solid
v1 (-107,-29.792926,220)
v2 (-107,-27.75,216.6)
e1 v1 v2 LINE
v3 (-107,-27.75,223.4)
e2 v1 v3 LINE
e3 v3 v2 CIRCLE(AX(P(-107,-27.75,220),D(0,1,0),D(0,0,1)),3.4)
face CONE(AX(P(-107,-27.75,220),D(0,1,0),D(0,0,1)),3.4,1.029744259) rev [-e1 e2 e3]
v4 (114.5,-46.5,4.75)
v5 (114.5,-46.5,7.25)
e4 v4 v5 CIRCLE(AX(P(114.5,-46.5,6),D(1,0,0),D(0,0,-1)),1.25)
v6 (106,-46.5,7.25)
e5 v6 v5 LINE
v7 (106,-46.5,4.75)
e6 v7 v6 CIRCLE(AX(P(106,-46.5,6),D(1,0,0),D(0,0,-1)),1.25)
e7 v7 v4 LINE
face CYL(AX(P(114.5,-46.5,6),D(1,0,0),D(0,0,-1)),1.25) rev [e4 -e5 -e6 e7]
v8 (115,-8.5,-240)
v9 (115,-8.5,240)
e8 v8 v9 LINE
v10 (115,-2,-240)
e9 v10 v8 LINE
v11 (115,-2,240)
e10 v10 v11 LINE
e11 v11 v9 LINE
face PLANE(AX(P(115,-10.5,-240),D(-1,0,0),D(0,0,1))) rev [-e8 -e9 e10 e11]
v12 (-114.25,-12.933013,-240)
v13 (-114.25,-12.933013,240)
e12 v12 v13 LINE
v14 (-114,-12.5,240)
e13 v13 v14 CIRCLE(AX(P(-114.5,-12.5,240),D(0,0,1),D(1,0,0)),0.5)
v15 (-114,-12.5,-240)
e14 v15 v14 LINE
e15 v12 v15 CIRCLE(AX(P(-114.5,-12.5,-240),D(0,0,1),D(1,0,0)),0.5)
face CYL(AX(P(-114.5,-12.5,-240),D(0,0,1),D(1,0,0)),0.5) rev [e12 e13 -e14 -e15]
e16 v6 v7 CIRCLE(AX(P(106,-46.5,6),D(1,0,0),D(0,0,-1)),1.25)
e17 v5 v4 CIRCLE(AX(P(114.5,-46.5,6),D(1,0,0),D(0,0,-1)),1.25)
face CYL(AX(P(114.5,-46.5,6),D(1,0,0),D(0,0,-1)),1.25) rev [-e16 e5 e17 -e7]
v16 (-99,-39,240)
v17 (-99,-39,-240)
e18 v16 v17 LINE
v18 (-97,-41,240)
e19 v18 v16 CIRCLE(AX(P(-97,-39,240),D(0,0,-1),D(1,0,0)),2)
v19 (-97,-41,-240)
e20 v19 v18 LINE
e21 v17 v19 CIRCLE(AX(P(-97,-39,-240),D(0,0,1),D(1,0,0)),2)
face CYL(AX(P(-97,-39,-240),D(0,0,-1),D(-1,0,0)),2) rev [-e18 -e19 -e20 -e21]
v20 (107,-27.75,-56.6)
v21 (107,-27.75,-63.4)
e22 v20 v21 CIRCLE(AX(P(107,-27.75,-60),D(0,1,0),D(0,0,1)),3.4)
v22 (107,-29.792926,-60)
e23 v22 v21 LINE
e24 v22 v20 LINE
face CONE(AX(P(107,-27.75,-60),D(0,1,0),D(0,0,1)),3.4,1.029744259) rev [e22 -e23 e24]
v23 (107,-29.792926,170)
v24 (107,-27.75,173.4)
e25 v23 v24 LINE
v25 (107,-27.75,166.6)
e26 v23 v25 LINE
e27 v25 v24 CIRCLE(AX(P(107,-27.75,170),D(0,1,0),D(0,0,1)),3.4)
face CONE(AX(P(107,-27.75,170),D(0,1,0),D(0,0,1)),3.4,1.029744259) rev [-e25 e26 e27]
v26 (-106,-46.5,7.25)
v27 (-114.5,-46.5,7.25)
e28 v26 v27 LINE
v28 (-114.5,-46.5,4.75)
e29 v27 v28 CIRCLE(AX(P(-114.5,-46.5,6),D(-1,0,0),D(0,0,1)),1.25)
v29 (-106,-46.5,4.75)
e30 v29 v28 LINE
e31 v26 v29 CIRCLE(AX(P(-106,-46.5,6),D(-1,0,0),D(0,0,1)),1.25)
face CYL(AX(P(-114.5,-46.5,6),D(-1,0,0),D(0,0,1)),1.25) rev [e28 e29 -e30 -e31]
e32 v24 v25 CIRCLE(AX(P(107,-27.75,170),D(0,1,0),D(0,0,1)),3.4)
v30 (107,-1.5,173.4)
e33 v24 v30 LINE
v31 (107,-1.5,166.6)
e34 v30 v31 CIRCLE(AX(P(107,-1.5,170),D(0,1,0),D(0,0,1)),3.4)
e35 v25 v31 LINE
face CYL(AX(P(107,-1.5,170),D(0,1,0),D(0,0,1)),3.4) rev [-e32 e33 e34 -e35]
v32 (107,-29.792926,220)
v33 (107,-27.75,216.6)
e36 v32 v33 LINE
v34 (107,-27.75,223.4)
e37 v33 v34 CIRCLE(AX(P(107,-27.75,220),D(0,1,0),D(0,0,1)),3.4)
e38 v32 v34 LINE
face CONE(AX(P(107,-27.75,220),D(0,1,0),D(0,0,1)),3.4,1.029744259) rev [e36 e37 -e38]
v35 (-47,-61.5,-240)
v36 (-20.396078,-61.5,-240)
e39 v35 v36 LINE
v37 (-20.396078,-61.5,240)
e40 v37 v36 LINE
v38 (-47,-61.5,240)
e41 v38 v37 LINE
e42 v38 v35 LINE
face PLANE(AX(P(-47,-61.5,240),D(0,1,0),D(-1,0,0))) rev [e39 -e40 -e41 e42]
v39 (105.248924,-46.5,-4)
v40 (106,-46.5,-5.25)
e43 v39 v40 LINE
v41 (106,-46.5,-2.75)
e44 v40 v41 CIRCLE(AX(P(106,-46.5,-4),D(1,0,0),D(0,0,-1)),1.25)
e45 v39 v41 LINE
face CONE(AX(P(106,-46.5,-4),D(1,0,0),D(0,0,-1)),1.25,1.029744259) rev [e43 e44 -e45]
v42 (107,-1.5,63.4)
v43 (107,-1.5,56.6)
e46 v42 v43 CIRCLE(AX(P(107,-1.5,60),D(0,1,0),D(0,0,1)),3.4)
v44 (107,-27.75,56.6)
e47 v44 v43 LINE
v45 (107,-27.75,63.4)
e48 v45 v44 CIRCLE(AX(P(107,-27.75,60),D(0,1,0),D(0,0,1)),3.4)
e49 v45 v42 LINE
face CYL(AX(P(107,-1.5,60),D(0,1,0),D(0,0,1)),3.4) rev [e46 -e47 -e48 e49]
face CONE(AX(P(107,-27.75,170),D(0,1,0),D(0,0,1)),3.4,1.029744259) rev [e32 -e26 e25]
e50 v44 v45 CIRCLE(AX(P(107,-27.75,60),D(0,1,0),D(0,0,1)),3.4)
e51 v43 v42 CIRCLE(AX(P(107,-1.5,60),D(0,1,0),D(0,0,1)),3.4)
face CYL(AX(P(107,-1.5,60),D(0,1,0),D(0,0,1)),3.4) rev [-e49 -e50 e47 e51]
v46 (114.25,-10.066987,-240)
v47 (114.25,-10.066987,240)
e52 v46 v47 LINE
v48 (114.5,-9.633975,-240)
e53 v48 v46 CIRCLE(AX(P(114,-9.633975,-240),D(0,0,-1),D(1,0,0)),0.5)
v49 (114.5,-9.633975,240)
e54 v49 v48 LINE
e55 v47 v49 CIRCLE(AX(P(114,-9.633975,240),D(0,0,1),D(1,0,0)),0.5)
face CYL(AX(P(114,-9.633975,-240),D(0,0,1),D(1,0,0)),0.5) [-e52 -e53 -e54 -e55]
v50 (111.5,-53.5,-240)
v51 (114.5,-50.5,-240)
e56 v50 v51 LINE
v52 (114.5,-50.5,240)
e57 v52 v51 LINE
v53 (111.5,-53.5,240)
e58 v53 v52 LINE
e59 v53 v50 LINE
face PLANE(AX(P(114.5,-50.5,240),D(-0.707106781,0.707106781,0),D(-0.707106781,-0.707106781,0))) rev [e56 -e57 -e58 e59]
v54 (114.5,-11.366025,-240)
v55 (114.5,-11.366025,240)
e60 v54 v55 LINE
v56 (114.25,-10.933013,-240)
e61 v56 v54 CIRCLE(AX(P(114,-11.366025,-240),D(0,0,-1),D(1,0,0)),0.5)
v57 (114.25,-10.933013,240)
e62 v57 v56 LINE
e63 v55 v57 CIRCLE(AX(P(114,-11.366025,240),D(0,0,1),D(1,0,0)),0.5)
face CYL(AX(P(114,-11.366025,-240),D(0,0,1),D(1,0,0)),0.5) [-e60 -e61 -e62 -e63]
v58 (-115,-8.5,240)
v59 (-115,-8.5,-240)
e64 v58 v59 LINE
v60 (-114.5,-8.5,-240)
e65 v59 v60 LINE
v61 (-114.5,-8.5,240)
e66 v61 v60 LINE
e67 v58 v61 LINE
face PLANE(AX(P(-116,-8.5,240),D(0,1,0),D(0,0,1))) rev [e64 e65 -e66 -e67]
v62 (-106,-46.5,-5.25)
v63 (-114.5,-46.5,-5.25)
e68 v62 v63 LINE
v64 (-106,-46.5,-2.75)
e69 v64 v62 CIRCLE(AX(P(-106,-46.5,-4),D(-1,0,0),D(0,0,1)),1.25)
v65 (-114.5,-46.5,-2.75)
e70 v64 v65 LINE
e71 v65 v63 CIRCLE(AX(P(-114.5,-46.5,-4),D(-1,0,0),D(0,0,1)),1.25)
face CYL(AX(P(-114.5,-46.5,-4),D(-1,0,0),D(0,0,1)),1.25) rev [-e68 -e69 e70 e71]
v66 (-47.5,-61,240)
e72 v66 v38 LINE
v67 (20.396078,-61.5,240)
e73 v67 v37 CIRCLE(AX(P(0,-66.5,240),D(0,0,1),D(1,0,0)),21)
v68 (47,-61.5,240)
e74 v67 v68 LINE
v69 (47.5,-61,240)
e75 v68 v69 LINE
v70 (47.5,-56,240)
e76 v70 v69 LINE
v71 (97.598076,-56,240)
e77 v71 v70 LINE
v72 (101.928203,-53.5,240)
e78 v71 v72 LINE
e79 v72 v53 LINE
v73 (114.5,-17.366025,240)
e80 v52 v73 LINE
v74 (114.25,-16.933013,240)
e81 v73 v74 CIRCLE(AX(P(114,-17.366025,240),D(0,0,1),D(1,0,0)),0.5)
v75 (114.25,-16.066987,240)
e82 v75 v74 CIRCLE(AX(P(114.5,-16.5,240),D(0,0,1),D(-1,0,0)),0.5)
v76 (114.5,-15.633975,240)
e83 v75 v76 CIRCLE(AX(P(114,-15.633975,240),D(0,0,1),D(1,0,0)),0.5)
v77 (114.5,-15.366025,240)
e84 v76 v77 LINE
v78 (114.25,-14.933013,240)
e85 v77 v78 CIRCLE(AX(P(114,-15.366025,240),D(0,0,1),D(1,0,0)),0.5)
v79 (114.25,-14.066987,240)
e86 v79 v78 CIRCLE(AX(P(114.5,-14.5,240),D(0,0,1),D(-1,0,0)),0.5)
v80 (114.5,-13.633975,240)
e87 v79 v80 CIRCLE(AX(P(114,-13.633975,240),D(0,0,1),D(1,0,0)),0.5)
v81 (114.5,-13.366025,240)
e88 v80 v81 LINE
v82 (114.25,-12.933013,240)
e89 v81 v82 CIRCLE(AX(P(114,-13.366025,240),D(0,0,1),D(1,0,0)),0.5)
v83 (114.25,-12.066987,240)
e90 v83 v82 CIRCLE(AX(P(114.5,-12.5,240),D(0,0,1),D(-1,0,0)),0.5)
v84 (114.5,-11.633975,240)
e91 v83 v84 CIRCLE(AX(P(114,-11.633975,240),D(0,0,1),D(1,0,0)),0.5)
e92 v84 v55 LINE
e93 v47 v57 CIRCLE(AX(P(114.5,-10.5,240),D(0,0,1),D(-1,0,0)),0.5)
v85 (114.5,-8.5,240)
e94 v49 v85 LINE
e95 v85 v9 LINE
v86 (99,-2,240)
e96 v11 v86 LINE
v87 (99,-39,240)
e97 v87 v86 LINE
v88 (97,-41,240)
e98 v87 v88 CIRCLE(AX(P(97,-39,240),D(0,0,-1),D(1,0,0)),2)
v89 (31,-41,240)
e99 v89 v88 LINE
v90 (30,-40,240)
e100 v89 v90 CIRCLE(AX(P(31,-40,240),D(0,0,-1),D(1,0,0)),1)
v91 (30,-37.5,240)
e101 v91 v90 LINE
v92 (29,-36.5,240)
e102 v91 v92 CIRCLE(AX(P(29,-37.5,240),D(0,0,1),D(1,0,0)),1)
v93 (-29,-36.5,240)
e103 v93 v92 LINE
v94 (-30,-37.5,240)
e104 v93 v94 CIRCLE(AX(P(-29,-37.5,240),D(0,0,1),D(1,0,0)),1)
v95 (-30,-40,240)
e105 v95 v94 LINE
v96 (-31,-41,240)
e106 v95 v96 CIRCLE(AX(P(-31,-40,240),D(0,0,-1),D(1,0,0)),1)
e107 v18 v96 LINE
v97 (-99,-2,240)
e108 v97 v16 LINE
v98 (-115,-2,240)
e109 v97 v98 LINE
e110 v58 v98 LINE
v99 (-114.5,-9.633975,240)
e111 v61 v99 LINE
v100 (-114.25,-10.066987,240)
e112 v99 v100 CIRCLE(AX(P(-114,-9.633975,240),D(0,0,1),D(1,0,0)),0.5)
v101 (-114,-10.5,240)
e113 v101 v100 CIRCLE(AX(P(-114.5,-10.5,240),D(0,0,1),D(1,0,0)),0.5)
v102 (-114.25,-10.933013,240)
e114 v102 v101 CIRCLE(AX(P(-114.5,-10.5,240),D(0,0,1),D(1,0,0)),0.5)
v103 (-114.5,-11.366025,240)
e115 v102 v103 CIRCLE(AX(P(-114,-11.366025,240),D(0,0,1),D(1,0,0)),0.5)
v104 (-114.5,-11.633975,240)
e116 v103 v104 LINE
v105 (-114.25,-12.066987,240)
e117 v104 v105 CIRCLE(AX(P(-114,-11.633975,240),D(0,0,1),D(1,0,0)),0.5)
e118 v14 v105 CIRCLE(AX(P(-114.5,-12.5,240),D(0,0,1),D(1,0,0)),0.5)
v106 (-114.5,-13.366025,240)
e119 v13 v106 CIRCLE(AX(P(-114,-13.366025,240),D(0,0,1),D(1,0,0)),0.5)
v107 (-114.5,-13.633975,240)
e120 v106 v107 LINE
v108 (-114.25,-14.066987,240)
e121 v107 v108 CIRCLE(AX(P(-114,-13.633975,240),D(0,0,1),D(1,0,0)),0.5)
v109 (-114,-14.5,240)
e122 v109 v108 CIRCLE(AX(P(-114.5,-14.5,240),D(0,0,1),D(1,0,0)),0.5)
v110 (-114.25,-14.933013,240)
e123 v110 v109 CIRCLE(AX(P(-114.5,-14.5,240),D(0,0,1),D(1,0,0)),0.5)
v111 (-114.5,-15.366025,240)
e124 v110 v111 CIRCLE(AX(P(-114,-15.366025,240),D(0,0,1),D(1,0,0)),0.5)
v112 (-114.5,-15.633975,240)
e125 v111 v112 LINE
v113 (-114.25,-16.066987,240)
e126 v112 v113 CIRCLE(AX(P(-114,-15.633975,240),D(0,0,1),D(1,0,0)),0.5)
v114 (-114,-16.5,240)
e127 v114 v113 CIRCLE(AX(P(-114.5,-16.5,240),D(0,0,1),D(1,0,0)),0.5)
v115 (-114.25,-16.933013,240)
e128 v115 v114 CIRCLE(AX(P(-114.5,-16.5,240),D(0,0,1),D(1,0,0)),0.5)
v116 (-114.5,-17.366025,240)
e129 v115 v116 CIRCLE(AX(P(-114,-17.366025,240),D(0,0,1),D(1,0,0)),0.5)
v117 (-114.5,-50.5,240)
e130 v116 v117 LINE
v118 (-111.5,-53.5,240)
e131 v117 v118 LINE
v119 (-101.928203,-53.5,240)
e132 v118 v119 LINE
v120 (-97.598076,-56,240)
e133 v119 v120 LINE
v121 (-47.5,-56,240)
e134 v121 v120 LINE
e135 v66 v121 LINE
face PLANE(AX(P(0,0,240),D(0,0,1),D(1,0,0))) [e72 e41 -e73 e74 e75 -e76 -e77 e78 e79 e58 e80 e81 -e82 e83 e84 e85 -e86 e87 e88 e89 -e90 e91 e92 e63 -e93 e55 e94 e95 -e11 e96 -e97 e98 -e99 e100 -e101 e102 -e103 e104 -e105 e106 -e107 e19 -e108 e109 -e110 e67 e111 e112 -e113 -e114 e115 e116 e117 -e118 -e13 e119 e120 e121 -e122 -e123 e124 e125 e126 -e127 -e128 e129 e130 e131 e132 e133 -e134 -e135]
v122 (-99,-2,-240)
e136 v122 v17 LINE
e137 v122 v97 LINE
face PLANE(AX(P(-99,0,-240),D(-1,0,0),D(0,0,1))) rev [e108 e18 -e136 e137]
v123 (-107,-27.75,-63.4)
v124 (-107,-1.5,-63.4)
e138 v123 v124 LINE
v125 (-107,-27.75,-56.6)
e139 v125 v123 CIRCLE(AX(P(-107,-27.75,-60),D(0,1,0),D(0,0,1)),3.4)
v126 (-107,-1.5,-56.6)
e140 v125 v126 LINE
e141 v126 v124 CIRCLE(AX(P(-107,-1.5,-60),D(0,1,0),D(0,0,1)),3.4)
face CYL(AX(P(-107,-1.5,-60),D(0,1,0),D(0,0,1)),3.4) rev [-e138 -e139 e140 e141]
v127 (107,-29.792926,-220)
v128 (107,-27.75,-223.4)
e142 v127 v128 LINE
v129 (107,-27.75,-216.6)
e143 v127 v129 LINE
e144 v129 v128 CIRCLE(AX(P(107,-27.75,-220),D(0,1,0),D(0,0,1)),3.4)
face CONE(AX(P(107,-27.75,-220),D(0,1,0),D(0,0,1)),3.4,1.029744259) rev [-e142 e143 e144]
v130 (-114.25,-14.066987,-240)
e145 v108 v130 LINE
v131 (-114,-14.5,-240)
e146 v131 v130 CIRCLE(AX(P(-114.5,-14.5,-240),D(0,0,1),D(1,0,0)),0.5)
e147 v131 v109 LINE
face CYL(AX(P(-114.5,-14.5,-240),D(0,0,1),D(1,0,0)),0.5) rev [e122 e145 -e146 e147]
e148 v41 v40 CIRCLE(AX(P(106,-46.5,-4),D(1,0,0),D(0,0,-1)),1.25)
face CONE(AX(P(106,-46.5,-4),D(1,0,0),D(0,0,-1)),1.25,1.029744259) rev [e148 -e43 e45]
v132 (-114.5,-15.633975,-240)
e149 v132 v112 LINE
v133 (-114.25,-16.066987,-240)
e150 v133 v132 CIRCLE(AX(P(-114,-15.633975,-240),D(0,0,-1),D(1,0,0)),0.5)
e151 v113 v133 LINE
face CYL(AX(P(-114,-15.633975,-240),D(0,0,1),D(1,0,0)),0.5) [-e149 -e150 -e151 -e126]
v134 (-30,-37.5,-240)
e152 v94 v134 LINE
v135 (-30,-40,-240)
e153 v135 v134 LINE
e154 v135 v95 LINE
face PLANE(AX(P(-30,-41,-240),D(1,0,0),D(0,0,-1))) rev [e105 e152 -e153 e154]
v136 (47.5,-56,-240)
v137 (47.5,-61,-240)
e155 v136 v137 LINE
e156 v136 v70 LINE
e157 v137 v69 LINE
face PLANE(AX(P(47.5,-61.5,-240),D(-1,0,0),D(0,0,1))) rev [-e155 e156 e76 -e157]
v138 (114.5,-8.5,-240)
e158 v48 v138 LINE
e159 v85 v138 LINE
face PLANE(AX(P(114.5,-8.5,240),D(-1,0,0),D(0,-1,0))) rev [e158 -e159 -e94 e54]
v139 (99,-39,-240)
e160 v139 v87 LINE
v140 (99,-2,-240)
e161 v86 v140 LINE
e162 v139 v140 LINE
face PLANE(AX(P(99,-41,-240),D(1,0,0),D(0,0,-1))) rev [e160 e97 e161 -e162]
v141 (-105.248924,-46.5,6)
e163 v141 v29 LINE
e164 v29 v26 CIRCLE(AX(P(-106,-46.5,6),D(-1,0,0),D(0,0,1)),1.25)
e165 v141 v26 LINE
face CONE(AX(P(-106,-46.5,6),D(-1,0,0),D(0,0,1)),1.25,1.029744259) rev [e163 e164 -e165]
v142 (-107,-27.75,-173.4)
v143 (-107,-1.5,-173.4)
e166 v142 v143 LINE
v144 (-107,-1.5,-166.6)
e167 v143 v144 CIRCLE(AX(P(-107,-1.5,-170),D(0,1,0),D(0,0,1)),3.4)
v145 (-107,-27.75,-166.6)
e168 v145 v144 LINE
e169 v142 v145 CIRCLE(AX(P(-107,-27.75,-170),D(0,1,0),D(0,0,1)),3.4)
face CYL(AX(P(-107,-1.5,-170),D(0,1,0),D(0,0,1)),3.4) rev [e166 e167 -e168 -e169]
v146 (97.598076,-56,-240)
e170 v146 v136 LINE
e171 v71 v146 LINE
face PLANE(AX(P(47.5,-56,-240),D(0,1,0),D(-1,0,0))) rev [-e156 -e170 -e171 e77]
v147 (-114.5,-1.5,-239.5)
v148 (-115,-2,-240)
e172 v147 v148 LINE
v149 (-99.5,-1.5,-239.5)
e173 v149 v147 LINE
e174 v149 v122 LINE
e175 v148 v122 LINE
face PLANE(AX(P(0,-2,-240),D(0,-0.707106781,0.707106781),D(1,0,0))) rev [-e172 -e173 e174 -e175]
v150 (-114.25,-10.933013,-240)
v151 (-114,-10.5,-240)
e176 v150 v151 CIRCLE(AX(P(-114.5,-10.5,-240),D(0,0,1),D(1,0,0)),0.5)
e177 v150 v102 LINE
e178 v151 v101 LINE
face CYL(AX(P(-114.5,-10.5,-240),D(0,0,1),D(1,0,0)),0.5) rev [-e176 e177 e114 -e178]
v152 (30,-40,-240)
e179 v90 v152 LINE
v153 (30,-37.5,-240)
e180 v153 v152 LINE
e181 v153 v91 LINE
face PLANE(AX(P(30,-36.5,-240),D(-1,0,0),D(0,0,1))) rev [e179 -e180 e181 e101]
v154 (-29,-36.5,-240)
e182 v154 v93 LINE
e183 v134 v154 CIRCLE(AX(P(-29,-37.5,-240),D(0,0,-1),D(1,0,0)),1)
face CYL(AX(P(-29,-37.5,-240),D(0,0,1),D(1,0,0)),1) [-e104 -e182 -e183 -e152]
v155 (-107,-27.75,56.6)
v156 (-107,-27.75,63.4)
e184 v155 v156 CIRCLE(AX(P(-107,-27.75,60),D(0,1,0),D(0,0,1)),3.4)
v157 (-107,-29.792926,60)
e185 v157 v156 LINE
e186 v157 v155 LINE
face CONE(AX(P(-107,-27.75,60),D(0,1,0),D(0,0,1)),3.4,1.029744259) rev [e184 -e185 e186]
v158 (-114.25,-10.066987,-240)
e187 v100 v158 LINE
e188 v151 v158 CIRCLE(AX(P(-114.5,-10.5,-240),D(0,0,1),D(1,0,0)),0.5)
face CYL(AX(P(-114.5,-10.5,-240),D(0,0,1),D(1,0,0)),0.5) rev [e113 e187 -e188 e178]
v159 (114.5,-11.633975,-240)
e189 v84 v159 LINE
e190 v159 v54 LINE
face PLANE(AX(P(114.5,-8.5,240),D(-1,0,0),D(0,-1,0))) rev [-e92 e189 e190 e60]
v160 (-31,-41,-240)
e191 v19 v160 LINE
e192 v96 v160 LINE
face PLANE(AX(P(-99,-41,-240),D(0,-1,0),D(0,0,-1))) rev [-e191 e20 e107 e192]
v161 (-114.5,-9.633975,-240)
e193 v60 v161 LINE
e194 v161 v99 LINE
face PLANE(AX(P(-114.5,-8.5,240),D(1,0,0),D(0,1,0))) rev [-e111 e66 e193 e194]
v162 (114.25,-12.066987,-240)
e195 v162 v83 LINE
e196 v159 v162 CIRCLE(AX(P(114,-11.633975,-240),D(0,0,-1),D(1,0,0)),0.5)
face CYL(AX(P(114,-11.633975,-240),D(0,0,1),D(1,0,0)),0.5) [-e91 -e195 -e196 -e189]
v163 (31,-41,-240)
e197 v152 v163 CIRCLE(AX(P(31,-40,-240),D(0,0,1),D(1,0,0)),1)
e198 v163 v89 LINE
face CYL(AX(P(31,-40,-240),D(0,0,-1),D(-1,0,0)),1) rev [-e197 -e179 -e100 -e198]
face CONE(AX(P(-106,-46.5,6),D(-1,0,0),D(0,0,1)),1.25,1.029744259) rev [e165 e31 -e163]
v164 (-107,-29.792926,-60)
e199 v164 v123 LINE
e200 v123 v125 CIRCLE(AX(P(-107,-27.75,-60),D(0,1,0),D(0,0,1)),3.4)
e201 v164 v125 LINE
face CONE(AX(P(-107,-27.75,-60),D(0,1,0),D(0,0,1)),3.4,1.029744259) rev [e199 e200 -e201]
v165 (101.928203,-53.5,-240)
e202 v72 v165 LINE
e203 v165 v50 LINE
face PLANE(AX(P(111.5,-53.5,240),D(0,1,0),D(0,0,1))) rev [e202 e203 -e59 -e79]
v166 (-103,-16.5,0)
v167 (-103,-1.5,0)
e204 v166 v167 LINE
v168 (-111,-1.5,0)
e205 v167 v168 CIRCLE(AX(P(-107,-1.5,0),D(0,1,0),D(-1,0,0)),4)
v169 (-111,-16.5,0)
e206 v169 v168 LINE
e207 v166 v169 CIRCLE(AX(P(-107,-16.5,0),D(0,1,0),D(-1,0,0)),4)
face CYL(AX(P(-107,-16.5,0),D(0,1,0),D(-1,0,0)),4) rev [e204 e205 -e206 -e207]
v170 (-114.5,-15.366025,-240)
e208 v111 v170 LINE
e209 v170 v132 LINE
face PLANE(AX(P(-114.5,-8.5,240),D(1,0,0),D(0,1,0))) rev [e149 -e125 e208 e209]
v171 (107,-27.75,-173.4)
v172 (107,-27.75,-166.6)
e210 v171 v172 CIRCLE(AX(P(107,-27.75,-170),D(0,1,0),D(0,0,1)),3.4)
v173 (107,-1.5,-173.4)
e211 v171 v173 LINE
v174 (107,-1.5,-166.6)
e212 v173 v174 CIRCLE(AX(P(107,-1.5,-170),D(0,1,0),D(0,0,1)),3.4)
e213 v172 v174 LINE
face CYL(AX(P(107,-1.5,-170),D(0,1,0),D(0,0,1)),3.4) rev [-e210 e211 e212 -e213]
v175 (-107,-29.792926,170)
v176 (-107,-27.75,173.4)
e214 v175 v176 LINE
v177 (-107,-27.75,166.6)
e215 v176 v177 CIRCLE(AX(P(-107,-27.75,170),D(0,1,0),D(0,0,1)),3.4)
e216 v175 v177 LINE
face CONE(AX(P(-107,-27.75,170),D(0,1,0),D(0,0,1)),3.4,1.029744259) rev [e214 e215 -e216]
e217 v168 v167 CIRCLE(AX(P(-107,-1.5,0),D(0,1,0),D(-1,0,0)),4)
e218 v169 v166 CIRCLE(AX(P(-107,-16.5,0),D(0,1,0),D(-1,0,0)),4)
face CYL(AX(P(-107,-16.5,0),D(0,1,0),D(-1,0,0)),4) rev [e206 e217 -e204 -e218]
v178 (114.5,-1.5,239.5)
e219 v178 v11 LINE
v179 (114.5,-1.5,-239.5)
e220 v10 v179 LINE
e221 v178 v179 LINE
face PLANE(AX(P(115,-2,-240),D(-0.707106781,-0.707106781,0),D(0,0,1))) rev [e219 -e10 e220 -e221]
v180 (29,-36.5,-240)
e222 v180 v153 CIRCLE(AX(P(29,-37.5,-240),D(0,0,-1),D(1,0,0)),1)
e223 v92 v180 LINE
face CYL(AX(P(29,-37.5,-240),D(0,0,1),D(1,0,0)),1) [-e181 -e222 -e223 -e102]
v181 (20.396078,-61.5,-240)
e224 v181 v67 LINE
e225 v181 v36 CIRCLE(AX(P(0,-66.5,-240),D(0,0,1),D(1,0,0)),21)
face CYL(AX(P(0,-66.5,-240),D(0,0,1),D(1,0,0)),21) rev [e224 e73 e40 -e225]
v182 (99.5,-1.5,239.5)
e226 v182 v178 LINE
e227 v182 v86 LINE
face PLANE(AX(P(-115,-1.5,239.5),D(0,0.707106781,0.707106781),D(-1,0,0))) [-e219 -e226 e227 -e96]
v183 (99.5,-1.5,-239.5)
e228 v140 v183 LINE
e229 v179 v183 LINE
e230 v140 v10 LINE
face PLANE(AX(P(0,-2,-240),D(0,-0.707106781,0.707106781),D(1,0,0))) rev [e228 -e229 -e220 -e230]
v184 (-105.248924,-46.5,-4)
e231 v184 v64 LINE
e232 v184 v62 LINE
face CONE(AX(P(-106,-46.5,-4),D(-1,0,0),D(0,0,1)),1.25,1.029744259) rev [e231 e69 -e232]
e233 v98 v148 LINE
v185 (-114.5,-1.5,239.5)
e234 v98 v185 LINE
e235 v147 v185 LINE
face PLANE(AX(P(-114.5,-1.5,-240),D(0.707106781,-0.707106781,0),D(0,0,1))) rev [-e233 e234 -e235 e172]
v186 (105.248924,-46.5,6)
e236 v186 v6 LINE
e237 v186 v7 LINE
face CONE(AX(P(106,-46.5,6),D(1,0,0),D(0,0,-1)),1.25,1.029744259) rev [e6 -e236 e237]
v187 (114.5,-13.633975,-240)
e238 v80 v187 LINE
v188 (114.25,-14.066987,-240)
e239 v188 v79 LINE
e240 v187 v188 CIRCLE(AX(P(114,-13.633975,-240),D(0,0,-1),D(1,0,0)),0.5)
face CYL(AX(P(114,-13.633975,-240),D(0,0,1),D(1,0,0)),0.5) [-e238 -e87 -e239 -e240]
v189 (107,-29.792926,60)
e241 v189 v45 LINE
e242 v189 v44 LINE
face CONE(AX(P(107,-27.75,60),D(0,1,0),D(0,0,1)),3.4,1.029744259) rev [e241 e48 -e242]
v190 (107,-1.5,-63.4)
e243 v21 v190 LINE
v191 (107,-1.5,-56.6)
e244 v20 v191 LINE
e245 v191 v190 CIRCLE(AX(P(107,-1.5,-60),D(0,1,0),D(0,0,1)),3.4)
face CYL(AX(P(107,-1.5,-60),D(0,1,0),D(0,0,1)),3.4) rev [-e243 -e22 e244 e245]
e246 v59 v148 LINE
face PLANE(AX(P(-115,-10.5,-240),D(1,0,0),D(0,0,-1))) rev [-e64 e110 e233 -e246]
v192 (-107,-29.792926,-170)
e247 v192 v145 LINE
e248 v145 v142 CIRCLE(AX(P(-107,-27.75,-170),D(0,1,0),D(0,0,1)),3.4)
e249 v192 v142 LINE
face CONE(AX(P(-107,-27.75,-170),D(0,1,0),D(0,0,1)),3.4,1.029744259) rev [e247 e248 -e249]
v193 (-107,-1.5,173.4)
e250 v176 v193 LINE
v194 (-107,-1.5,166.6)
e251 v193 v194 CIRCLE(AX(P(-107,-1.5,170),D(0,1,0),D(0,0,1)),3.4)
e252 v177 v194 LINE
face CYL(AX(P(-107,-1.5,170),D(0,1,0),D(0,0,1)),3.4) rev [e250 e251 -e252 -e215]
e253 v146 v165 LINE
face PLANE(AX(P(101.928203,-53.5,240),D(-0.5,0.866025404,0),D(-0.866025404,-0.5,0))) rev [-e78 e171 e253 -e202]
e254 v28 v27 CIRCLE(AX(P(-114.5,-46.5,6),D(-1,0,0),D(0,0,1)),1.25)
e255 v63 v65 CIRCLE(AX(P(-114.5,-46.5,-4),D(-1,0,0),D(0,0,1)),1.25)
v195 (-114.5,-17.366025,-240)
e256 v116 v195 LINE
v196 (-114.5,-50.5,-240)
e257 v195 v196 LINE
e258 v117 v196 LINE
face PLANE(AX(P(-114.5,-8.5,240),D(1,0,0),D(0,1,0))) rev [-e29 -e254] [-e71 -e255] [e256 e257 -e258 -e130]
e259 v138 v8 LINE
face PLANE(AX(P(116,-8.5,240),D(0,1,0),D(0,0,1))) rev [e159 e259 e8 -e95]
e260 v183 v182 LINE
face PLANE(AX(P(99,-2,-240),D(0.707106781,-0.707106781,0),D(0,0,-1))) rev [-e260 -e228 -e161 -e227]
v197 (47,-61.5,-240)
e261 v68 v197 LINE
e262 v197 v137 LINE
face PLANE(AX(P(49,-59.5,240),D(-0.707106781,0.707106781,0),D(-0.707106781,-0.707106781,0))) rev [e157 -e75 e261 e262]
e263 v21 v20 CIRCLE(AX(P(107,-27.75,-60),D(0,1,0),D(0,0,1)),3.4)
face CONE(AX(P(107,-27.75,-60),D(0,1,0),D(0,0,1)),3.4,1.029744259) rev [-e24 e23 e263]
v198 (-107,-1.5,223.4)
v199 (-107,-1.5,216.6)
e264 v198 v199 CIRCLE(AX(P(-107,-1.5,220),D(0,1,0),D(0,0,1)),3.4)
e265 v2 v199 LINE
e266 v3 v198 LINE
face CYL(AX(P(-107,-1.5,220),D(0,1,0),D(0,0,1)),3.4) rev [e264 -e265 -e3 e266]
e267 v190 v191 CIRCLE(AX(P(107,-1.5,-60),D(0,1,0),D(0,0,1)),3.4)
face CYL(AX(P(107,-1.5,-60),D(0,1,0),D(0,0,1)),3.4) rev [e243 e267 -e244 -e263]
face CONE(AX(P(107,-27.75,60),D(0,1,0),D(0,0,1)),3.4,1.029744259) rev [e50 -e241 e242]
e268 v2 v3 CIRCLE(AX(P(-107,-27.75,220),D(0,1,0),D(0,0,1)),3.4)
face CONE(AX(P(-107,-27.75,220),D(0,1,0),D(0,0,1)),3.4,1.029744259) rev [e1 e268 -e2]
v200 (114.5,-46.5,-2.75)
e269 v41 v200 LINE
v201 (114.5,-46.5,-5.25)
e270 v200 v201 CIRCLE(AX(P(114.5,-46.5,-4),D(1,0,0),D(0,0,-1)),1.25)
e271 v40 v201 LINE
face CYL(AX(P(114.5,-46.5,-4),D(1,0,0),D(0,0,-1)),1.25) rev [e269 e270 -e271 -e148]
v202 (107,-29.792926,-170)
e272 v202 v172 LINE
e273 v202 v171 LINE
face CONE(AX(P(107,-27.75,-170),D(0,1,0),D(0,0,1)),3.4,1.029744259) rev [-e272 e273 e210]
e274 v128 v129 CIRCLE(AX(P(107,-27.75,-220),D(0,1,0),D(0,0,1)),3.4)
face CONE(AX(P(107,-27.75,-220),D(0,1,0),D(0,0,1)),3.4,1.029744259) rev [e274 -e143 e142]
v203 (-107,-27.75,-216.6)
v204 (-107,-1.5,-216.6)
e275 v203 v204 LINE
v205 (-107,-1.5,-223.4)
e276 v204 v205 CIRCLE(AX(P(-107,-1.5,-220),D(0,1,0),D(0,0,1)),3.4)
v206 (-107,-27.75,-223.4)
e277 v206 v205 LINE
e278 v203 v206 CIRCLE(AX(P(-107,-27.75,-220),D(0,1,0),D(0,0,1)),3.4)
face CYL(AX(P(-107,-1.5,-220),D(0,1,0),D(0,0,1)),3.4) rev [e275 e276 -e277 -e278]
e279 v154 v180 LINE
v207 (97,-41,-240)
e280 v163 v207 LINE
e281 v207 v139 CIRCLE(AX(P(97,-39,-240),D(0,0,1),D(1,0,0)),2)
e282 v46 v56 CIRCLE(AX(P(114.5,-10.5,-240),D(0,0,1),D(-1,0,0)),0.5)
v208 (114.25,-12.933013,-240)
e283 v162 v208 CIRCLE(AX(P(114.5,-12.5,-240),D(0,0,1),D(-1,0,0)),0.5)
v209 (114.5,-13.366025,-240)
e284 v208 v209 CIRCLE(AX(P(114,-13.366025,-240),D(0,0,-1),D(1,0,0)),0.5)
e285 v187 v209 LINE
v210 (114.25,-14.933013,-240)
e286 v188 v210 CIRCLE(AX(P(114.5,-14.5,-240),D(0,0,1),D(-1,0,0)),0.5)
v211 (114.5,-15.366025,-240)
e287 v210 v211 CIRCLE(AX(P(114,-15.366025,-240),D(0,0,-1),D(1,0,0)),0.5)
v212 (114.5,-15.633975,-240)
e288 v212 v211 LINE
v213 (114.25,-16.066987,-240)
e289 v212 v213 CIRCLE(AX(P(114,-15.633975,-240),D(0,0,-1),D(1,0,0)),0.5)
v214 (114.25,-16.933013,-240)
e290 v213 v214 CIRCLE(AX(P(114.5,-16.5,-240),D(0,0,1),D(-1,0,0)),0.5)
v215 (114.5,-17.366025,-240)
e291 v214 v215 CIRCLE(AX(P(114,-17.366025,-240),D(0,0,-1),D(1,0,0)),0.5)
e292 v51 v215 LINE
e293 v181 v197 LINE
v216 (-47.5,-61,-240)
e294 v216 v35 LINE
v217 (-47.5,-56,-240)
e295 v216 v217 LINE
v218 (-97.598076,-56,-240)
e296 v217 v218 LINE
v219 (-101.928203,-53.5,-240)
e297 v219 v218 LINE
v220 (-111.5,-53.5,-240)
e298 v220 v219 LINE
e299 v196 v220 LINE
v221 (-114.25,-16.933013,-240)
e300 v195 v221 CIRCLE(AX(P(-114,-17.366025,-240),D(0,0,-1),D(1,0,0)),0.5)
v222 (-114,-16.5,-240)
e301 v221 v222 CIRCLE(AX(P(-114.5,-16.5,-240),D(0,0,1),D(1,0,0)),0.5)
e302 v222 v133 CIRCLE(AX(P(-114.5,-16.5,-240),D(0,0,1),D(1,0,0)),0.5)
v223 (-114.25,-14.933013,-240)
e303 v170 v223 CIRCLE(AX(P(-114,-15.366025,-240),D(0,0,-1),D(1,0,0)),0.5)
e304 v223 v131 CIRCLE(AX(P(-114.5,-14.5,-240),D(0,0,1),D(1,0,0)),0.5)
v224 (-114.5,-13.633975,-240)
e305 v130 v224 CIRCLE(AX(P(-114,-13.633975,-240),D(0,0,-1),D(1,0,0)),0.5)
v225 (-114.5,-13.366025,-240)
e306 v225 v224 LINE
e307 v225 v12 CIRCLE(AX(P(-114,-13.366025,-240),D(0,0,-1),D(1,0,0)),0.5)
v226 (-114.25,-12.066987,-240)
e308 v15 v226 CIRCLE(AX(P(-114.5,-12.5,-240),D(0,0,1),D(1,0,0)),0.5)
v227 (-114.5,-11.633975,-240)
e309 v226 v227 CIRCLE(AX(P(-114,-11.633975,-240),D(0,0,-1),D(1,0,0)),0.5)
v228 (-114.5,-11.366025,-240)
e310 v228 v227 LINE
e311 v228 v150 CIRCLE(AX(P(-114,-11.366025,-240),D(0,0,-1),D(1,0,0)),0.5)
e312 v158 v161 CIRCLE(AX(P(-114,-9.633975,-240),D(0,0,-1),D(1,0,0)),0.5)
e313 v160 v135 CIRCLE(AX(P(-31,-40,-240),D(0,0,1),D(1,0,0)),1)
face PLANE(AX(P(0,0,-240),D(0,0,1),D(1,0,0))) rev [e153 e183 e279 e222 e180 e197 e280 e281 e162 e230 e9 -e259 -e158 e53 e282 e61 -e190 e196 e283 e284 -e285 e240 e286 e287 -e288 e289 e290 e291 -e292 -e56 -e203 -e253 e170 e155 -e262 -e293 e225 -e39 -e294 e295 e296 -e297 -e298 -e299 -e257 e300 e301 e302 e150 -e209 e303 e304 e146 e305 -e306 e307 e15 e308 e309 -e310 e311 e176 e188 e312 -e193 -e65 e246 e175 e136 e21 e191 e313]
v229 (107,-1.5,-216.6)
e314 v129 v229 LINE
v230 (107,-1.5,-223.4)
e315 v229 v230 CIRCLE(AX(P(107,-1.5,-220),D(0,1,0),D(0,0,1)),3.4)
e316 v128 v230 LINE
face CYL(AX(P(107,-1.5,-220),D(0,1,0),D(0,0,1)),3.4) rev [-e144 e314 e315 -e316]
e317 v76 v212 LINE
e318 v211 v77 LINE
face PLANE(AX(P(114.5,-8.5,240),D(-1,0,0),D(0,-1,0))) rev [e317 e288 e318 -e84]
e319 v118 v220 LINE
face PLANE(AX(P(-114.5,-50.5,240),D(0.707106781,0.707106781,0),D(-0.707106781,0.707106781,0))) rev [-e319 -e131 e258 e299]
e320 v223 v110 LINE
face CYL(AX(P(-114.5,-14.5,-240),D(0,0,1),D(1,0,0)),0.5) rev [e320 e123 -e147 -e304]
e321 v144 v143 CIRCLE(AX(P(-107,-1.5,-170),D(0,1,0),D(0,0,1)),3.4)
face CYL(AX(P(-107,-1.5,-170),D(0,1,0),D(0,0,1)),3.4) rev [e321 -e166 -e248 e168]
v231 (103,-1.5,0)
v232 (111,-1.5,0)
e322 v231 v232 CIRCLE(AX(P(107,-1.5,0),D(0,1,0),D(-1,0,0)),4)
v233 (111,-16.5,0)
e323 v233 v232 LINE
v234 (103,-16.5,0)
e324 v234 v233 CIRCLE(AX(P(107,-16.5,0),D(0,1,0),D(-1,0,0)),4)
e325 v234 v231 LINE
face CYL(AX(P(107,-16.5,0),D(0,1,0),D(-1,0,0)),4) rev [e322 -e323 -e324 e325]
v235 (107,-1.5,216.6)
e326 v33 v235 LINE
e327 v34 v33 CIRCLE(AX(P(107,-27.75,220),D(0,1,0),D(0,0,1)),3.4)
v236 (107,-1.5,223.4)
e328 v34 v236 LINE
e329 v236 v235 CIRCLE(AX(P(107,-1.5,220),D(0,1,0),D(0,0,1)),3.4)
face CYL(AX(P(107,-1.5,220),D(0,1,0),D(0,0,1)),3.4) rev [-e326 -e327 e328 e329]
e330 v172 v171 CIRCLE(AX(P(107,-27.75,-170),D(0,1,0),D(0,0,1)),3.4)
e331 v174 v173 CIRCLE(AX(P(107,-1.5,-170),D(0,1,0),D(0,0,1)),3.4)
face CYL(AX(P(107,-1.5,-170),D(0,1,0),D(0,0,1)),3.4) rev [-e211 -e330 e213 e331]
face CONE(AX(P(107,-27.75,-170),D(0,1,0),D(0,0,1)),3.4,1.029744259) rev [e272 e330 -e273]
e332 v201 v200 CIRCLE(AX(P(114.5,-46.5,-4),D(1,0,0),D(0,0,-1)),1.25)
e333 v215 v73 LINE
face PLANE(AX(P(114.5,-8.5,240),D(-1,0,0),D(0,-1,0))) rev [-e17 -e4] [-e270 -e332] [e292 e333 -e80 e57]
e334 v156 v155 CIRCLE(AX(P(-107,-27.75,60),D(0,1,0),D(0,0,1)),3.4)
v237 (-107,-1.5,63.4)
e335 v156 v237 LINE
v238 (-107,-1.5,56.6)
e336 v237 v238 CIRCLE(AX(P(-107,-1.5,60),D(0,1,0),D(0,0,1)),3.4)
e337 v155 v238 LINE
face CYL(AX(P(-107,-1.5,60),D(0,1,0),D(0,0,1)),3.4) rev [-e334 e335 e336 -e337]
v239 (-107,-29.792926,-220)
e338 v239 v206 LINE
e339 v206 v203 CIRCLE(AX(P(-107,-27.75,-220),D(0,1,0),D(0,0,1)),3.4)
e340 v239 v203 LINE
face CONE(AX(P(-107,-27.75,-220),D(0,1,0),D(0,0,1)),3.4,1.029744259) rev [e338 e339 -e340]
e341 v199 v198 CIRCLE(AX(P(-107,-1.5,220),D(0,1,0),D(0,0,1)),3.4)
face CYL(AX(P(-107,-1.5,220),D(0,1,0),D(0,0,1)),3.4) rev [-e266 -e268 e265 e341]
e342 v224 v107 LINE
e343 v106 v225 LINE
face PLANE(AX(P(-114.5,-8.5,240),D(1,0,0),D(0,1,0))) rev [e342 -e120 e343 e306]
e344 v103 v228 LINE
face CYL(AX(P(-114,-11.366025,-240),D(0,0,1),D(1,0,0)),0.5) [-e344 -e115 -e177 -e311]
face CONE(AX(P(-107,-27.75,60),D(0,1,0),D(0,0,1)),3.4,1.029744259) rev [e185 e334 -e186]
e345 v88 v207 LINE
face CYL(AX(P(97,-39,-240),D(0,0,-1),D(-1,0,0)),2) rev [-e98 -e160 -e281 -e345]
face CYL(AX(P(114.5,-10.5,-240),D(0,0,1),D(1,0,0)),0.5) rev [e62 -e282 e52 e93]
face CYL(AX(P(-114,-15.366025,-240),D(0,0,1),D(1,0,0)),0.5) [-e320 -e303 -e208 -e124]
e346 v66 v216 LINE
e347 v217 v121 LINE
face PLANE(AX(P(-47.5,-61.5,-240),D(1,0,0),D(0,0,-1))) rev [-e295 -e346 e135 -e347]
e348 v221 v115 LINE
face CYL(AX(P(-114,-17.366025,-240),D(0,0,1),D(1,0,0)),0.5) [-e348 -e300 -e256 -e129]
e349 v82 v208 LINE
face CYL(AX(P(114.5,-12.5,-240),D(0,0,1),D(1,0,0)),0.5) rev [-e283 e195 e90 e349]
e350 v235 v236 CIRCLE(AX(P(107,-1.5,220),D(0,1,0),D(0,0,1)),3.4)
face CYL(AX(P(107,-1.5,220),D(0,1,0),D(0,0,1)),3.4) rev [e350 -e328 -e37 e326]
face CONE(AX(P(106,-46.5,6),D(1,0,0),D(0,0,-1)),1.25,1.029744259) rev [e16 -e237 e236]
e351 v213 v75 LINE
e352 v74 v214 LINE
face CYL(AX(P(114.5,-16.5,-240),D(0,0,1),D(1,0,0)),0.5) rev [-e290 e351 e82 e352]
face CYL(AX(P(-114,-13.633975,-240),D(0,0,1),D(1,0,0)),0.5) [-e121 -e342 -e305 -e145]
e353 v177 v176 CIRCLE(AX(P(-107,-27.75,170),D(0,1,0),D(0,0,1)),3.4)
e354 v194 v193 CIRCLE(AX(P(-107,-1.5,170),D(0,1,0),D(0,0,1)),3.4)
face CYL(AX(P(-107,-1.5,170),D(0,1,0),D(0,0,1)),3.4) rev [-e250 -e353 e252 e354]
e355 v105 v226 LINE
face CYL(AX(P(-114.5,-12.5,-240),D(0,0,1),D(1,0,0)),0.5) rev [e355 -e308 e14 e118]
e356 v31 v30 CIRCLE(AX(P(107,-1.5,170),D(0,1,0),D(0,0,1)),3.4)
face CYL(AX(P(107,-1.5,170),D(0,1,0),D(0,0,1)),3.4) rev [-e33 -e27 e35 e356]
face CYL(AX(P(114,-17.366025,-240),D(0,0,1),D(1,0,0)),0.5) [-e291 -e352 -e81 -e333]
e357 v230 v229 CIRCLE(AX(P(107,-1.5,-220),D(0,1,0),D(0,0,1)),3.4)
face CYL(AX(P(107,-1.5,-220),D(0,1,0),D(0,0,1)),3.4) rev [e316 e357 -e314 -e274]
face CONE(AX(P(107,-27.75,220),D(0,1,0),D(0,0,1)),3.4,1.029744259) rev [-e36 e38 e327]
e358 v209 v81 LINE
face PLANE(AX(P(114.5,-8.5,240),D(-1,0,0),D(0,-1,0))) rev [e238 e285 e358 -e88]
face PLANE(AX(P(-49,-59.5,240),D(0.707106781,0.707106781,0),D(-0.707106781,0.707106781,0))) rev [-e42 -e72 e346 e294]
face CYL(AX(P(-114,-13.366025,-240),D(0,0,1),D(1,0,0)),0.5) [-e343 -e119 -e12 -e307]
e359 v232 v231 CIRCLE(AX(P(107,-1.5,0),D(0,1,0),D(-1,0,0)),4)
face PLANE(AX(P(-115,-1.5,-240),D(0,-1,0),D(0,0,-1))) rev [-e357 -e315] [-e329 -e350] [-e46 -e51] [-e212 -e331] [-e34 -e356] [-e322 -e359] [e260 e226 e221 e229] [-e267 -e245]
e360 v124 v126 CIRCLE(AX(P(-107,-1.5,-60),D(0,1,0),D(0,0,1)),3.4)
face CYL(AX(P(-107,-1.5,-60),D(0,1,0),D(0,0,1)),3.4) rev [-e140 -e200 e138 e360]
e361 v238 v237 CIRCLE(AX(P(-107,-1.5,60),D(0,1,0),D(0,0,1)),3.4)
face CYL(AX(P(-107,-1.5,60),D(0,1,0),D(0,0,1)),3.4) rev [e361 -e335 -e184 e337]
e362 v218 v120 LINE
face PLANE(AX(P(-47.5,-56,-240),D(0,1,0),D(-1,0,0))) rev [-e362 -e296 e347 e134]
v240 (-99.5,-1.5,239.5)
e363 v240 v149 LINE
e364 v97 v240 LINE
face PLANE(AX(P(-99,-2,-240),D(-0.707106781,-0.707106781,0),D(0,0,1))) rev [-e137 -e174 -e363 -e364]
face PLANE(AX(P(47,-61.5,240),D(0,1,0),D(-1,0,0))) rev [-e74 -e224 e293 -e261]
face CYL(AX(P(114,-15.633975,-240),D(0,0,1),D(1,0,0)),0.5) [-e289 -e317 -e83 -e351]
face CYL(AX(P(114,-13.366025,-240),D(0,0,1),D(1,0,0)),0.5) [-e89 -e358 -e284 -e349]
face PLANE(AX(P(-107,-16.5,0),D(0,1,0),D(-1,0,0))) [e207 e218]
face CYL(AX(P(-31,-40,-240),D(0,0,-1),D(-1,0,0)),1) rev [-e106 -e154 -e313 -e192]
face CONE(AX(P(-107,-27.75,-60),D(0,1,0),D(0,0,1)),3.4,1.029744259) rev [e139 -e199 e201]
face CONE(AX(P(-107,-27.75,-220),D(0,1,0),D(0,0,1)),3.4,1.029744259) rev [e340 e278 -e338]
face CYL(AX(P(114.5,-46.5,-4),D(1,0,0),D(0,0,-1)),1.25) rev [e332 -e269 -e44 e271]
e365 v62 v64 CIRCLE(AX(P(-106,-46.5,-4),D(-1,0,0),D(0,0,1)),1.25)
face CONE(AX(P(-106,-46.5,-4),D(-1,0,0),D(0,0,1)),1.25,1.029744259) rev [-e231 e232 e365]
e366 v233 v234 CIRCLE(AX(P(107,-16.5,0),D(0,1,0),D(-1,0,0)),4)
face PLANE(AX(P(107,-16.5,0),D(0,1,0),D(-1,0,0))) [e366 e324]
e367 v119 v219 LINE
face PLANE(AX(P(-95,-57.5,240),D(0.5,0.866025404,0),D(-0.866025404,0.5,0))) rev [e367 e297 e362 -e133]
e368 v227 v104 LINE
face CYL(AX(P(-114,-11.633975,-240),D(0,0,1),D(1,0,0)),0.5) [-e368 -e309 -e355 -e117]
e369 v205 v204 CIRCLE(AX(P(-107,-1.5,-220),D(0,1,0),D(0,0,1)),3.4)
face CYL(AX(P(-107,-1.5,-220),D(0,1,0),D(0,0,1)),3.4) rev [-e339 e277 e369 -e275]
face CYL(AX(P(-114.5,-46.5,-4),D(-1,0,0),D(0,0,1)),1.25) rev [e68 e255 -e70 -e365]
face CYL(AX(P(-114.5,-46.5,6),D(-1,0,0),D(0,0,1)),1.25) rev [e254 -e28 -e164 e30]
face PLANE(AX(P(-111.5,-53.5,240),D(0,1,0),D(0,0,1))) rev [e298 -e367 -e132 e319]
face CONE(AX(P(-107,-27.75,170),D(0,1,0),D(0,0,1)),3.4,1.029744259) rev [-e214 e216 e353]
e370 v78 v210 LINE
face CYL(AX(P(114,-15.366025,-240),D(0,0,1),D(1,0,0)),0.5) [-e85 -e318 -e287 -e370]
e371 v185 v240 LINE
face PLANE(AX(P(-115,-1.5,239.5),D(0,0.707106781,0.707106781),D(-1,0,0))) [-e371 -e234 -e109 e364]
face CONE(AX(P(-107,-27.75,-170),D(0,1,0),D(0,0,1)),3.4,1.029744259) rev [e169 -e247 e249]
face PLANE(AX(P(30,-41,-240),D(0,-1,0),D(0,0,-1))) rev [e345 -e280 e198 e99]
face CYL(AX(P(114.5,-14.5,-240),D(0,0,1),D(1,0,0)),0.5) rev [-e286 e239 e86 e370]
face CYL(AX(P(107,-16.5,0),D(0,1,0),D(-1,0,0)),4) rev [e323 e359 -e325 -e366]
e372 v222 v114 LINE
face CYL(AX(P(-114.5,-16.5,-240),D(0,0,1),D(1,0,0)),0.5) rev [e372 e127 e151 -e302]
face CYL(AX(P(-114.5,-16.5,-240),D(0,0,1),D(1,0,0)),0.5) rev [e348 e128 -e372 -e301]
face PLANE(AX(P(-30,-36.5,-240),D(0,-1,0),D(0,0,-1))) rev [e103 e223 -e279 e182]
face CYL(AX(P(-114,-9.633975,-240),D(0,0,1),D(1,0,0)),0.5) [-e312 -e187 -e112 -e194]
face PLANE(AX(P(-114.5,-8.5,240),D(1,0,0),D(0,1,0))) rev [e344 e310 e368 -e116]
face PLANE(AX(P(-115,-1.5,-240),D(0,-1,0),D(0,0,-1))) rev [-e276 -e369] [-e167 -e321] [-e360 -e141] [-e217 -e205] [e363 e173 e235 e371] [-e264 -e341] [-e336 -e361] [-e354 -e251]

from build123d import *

# Parameters (mm, degrees)
EXTRUDE_1_DEPTH             = 240
CUT_EXTRUDE_1_DEPTH         = 504.178149367
FILLET_1_R                  = 2
FILLET_8_R                  = 1
CUT_EXTRUDE_3_DEPTH         = 504.178149367
FILLET_6_R                  = 0.5
CUT_EXTRUDE_4_DEPTH         = 504.178149367
SKETCH_8_W                  = 1.5
SKETCH_8_H                  = 10.5
CUT_EXTRUDE_6496_DEPTH      = 504.178149367
SKETCH_9_W                  = 230
SKETCH_9_H                  = 1.5
CUT_EXTRUDE_6896_DEPTH      = 503.832974257
SKETCH_10_W                 = 67
SKETCH_10_H                 = 5.5
CUT_EXTRUDE_7625_DEPTH      = 503.832974257
SKETCH_31_W                 = 27
SKETCH_31_H                 = 3
CUT_EXTRUDE_10_DEPTH        = 503.832974257
HOLE_WIZARD_M8_1_D          = 6.8
HOLE_WIZARD_M8_1_DEPTH      = 26.25
HOLE_WIZARD_M8_1_TIP        = 2.042926105
SKETCH_22_R                 = 4
CUT_EXTRUDE_8_DEPTH         = 15
HOLE_WIZARD_M3_1_AT_2_COUNT = 2
HOLE_WIZARD_M3_1_AT_2_PITCH = 10
CHAMFER_3_SIZE              = 0.5
SKETCH_30_R                 = 5
CUT_EXTRUDE_9_DEPTH         = 6
SKETCH_32_W                 = 66
SKETCH_32_H                 = 34.5
CUT_EXTRUDE_11_DEPTH        = 503.832974257


with BuildPart() as part:
    # 草图1 → 凸台-拉伸1 (new, symmetric)
    with BuildSketch(Plane.XY):
        Polygon((-116.5, 0), (116.5, 0), (116.5, -8), (116, -8.5), (114.5, -8.5), (114.5, -50.5), (111.5, -53.5), (101.92820323, -53.5), (95, -57.5), (49, -57.5), (49, -59.5), (47, -61.5), (33, -61.5), (33, -86), (27.226497308, -96), (-27.226497308, -96), (-33, -86), (-33, -61.5), (-47, -61.5), (-49, -59.5), (-49, -57.5), (-95, -57.5), (-101.92820323, -53.5), (-111.5, -53.5), (-114.5, -50.5), (-114.5, -8.5), (-116, -8.5), (-116.5, -8), align=None)
    extrude(amount=EXTRUDE_1_DEPTH, both=True)

    # 草图2 → 切除-拉伸1 (cut, through all)
    with BuildSketch(Plane.XY.offset(240)):
        Polygon((-99, 0), (99, 0), (99, -41), (30, -41), (30, -36.5), (-30, -36.5), (-30, -41), (-99, -41), align=None)
    extrude(amount=-CUT_EXTRUDE_1_DEPTH, mode=Mode.SUBTRACT)

    # 圆角1
    fillet_1_edges = [part.edges().sort_by_distance(p)[0] for p in [
        (99, -41, 0),
        (-99, -41, 0),
    ]]
    fillet(fillet_1_edges, radius=FILLET_1_R)

    # 圆角8
    fillet_8_edges = [part.edges().sort_by_distance(p)[0] for p in [
        (30, -41, 0),
        (30, -36.5, 0),
        (-30, -36.5, 0),
        (-30, -41, 0),
    ]]
    fillet(fillet_8_edges, radius=FILLET_8_R)

    # 草图4 → 切除-拉伸3 (cut, through all)
    with BuildSketch(Plane.XY.offset(240)):
        with BuildLine():
            Line((-114.5, -10), (-114.5, -11))
            ThreePointArc((-114.5, -11), (-114, -10.5), (-114.5, -10))
        make_face()
        with BuildLine():
            Line((-114.5, -12), (-114.5, -13))
            ThreePointArc((-114.5, -13), (-114, -12.5), (-114.5, -12))
        make_face()
        with BuildLine():
            Line((-114.5, -14), (-114.5, -15))
            ThreePointArc((-114.5, -15), (-114, -14.5), (-114.5, -14))
        make_face()
        with BuildLine():
            Line((-114.5, -16), (-114.5, -17))
            ThreePointArc((-114.5, -17), (-114, -16.5), (-114.5, -16))
        make_face()
        with BuildLine():
            Line((114.5, -16), (114.5, -17))
            ThreePointArc((114.5, -17), (114, -16.5), (114.5, -16))
        make_face()
        with BuildLine():
            Line((114.5, -14), (114.5, -15))
            ThreePointArc((114.5, -15), (114, -14.5), (114.5, -14))
        make_face()
        with BuildLine():
            Line((114.5, -12), (114.5, -13))
            ThreePointArc((114.5, -13), (114, -12.5), (114.5, -12))
        make_face()
        with BuildLine():
            Line((114.5, -10), (114.5, -11))
            ThreePointArc((114.5, -11), (114, -10.5), (114.5, -10))
        make_face()
    extrude(amount=-CUT_EXTRUDE_3_DEPTH, mode=Mode.SUBTRACT)

    # 圆角6
    fillet_6_edges = [part.edges().sort_by_distance(p)[0] for p in [
        (-114.5, -14, 0),
        (-114.5, -15, 0),
        (-114.5, -12, 0),
        (-114.5, -13, 0),
        (-114.5, -16, 0),
        (-114.5, -17, 0),
        (-114.5, -10, 0),
        (-114.5, -11, 0),
        (114.5, -13, 0),
        (114.5, -12, 0),
        (114.5, -11, 0),
        (114.5, -10, 0),
        (114.5, -15, 0),
        (114.5, -14, 0),
        (114.5, -17, 0),
        (114.5, -16, 0),
    ]]
    fillet(fillet_6_edges, radius=FILLET_6_R)

    # 草图5 → 切除-拉伸4 (cut, through all)
    with BuildSketch(Plane.XY.offset(240)):
        with BuildLine():
            Line((-13.5, -82.585707942), (-13.5, -93))
            Line((-13.5, -93), (13.5, -93))
            Line((13.5, -93), (13.5, -82.585707942))
            ThreePointArc((13.5, -82.585707942), (0, -45.5), (-13.5, -82.585707942))
        make_face()
    extrude(amount=-CUT_EXTRUDE_4_DEPTH, mode=Mode.SUBTRACT)

    # 草图8 → Cut-Extrude 6496 (cut, through all)
    with BuildSketch(Plane.XY.offset(240)):
        with Locations((115.75, -5.25)):
            Rectangle(SKETCH_8_W, SKETCH_8_H)
        with Locations((-115.75, -5.25)):
            Rectangle(SKETCH_8_W, SKETCH_8_H)
    extrude(amount=-CUT_EXTRUDE_6496_DEPTH, mode=Mode.SUBTRACT)

    # 草图9 → Cut-Extrude 6896 (cut, through all)
    with BuildSketch(Plane.XY.offset(240)):
        with Locations((0, -0.75)):
            Rectangle(SKETCH_9_W, SKETCH_9_H)
    extrude(amount=-CUT_EXTRUDE_6896_DEPTH, mode=Mode.SUBTRACT)

    # 草图10 → Cut-Extrude 7625 (cut, through all)
    with BuildSketch(Plane.XY.offset(240)):
        with Locations((81, -58.75)):
            Rectangle(SKETCH_10_W, SKETCH_10_H)
        with Locations((-81, -58.75)):
            Rectangle(SKETCH_10_W, SKETCH_10_H)
    extrude(amount=-CUT_EXTRUDE_7625_DEPTH, mode=Mode.SUBTRACT)

    # 草图31 → 切除-拉伸10 (cut, through all)
    with BuildSketch(Plane.XY.offset(240)):
        with Locations((0, -94.5)):
            Rectangle(SKETCH_31_W, SKETCH_31_H)
    extrude(amount=-CUT_EXTRUDE_10_DEPTH, mode=Mode.SUBTRACT)

    # M8 螺纹孔1
    with Locations(Plane(origin=(0, -1.5, 0), x_dir=(1, 0, 0), z_dir=(0, 1, 0))):
        with Locations((-107, 60), (-107, -60), (107, -60), (107, 60), (107, 220), (107, -220), (-107, -220), (-107, 220), (107, 170), (107, -170), (-107, -170), (-107, 170)):
            Hole(HOLE_WIZARD_M8_1_D / 2, depth=HOLE_WIZARD_M8_1_DEPTH)
            with Locations((0, 0, -(HOLE_WIZARD_M8_1_DEPTH + HOLE_WIZARD_M8_1_TIP / 2))):  # 118° drill point
                Cone(0, HOLE_WIZARD_M8_1_D / 2, HOLE_WIZARD_M8_1_TIP, mode=Mode.SUBTRACT)

    # 草图22 → 切除-拉伸8 (cut)
    with BuildSketch(Plane(origin=(0, -1.5, 0), x_dir=(1, 0, 0), z_dir=(0, 1, 0))):
        with Locations(Location((-107, 0, 0), (0, 0, 180))):
            Circle(SKETCH_22_R)
        with Locations(Location((107, 0, 0), (0, 0, 180))):
            Circle(SKETCH_22_R)
    extrude(amount=-CUT_EXTRUDE_8_DEPTH, mode=Mode.SUBTRACT)

    # 草图28 → M3 螺纹孔1 (revolve, cut)
    with BuildSketch(Plane(origin=(114.5, -46.5, -4), x_dir=(0, 0, -1), z_dir=(0, 1, 0))):
        Polygon((0, 0), (0, 9.251075774), (1.25, 8.5), (1.25, 0), align=None)
    hole_wizard_m3_1 = revolve(axis=Axis((120.85, -46.5, -4), (-1, 0, 0)), mode=Mode.SUBTRACT)

    # M3 螺纹孔1 at 2: M3 螺纹孔1 ×2
    with Locations(*[(0, 0, i * HOLE_WIZARD_M3_1_AT_2_PITCH) for i in range(1, HOLE_WIZARD_M3_1_AT_2_COUNT)]):
        add(hole_wizard_m3_1, mode=Mode.SUBTRACT)

    # 镜向1: M3 螺纹孔1 across plane
    add(hole_wizard_m3_1.mirror(Plane(origin=(0, 0, 0), x_dir=(0, 0, 1), z_dir=(1, 0, 0))), mode=Mode.SUBTRACT)

    # 镜向1 copy 1 sketch → 镜向1 copy 1 (revolve, cut)
    with BuildSketch(Plane(origin=(-114.5, -46.5, 6), x_dir=(0, 0, -1), z_dir=(0, 1, 0))):
        Polygon((0, 0), (0, -9.251075774), (1.25, -8.5), (1.25, 0), align=None)
    revolve(axis=Axis((-120.85, -46.5, 6), (-1, 0, 0)), mode=Mode.SUBTRACT)

    # 倒角3
    chamfer_3_edges = [part.edges().sort_by_distance(p)[0] for p in [
        (99, -1.5, 0),
        (107, -1.5, -240),
        (115, -1.5, 0),
        (-107, -1.5, -240),
        (-99, -1.5, 0),
        (107, -1.5, 240),
        (-107, -1.5, 240),
        (-115, -1.5, 0),
    ]]
    chamfer(chamfer_3_edges, length=CHAMFER_3_SIZE)

    # 草图30 → 切除-拉伸9 (cut)
    with BuildSketch(Plane.XY.offset(240)):
        with Locations((-26.5, -66.5)):
            Circle(SKETCH_30_R)
        with Locations(Location((26.5, -66.5, 0), (0, 0, 180))):
            Circle(SKETCH_30_R)
    extrude(amount=-CUT_EXTRUDE_9_DEPTH, mode=Mode.SUBTRACT)

    # 草图32 → 切除-拉伸11 (cut, through all)
    with BuildSketch(Plane(origin=(0, 0, -240), x_dir=(-1, 0, 0), z_dir=(0, 0, -1))):
        with Locations((0, -78.75)):
            Rectangle(SKETCH_32_W, SKETCH_32_H)
    extrude(amount=-CUT_EXTRUDE_11_DEPTH, mode=Mode.SUBTRACT)


solid = part.part
